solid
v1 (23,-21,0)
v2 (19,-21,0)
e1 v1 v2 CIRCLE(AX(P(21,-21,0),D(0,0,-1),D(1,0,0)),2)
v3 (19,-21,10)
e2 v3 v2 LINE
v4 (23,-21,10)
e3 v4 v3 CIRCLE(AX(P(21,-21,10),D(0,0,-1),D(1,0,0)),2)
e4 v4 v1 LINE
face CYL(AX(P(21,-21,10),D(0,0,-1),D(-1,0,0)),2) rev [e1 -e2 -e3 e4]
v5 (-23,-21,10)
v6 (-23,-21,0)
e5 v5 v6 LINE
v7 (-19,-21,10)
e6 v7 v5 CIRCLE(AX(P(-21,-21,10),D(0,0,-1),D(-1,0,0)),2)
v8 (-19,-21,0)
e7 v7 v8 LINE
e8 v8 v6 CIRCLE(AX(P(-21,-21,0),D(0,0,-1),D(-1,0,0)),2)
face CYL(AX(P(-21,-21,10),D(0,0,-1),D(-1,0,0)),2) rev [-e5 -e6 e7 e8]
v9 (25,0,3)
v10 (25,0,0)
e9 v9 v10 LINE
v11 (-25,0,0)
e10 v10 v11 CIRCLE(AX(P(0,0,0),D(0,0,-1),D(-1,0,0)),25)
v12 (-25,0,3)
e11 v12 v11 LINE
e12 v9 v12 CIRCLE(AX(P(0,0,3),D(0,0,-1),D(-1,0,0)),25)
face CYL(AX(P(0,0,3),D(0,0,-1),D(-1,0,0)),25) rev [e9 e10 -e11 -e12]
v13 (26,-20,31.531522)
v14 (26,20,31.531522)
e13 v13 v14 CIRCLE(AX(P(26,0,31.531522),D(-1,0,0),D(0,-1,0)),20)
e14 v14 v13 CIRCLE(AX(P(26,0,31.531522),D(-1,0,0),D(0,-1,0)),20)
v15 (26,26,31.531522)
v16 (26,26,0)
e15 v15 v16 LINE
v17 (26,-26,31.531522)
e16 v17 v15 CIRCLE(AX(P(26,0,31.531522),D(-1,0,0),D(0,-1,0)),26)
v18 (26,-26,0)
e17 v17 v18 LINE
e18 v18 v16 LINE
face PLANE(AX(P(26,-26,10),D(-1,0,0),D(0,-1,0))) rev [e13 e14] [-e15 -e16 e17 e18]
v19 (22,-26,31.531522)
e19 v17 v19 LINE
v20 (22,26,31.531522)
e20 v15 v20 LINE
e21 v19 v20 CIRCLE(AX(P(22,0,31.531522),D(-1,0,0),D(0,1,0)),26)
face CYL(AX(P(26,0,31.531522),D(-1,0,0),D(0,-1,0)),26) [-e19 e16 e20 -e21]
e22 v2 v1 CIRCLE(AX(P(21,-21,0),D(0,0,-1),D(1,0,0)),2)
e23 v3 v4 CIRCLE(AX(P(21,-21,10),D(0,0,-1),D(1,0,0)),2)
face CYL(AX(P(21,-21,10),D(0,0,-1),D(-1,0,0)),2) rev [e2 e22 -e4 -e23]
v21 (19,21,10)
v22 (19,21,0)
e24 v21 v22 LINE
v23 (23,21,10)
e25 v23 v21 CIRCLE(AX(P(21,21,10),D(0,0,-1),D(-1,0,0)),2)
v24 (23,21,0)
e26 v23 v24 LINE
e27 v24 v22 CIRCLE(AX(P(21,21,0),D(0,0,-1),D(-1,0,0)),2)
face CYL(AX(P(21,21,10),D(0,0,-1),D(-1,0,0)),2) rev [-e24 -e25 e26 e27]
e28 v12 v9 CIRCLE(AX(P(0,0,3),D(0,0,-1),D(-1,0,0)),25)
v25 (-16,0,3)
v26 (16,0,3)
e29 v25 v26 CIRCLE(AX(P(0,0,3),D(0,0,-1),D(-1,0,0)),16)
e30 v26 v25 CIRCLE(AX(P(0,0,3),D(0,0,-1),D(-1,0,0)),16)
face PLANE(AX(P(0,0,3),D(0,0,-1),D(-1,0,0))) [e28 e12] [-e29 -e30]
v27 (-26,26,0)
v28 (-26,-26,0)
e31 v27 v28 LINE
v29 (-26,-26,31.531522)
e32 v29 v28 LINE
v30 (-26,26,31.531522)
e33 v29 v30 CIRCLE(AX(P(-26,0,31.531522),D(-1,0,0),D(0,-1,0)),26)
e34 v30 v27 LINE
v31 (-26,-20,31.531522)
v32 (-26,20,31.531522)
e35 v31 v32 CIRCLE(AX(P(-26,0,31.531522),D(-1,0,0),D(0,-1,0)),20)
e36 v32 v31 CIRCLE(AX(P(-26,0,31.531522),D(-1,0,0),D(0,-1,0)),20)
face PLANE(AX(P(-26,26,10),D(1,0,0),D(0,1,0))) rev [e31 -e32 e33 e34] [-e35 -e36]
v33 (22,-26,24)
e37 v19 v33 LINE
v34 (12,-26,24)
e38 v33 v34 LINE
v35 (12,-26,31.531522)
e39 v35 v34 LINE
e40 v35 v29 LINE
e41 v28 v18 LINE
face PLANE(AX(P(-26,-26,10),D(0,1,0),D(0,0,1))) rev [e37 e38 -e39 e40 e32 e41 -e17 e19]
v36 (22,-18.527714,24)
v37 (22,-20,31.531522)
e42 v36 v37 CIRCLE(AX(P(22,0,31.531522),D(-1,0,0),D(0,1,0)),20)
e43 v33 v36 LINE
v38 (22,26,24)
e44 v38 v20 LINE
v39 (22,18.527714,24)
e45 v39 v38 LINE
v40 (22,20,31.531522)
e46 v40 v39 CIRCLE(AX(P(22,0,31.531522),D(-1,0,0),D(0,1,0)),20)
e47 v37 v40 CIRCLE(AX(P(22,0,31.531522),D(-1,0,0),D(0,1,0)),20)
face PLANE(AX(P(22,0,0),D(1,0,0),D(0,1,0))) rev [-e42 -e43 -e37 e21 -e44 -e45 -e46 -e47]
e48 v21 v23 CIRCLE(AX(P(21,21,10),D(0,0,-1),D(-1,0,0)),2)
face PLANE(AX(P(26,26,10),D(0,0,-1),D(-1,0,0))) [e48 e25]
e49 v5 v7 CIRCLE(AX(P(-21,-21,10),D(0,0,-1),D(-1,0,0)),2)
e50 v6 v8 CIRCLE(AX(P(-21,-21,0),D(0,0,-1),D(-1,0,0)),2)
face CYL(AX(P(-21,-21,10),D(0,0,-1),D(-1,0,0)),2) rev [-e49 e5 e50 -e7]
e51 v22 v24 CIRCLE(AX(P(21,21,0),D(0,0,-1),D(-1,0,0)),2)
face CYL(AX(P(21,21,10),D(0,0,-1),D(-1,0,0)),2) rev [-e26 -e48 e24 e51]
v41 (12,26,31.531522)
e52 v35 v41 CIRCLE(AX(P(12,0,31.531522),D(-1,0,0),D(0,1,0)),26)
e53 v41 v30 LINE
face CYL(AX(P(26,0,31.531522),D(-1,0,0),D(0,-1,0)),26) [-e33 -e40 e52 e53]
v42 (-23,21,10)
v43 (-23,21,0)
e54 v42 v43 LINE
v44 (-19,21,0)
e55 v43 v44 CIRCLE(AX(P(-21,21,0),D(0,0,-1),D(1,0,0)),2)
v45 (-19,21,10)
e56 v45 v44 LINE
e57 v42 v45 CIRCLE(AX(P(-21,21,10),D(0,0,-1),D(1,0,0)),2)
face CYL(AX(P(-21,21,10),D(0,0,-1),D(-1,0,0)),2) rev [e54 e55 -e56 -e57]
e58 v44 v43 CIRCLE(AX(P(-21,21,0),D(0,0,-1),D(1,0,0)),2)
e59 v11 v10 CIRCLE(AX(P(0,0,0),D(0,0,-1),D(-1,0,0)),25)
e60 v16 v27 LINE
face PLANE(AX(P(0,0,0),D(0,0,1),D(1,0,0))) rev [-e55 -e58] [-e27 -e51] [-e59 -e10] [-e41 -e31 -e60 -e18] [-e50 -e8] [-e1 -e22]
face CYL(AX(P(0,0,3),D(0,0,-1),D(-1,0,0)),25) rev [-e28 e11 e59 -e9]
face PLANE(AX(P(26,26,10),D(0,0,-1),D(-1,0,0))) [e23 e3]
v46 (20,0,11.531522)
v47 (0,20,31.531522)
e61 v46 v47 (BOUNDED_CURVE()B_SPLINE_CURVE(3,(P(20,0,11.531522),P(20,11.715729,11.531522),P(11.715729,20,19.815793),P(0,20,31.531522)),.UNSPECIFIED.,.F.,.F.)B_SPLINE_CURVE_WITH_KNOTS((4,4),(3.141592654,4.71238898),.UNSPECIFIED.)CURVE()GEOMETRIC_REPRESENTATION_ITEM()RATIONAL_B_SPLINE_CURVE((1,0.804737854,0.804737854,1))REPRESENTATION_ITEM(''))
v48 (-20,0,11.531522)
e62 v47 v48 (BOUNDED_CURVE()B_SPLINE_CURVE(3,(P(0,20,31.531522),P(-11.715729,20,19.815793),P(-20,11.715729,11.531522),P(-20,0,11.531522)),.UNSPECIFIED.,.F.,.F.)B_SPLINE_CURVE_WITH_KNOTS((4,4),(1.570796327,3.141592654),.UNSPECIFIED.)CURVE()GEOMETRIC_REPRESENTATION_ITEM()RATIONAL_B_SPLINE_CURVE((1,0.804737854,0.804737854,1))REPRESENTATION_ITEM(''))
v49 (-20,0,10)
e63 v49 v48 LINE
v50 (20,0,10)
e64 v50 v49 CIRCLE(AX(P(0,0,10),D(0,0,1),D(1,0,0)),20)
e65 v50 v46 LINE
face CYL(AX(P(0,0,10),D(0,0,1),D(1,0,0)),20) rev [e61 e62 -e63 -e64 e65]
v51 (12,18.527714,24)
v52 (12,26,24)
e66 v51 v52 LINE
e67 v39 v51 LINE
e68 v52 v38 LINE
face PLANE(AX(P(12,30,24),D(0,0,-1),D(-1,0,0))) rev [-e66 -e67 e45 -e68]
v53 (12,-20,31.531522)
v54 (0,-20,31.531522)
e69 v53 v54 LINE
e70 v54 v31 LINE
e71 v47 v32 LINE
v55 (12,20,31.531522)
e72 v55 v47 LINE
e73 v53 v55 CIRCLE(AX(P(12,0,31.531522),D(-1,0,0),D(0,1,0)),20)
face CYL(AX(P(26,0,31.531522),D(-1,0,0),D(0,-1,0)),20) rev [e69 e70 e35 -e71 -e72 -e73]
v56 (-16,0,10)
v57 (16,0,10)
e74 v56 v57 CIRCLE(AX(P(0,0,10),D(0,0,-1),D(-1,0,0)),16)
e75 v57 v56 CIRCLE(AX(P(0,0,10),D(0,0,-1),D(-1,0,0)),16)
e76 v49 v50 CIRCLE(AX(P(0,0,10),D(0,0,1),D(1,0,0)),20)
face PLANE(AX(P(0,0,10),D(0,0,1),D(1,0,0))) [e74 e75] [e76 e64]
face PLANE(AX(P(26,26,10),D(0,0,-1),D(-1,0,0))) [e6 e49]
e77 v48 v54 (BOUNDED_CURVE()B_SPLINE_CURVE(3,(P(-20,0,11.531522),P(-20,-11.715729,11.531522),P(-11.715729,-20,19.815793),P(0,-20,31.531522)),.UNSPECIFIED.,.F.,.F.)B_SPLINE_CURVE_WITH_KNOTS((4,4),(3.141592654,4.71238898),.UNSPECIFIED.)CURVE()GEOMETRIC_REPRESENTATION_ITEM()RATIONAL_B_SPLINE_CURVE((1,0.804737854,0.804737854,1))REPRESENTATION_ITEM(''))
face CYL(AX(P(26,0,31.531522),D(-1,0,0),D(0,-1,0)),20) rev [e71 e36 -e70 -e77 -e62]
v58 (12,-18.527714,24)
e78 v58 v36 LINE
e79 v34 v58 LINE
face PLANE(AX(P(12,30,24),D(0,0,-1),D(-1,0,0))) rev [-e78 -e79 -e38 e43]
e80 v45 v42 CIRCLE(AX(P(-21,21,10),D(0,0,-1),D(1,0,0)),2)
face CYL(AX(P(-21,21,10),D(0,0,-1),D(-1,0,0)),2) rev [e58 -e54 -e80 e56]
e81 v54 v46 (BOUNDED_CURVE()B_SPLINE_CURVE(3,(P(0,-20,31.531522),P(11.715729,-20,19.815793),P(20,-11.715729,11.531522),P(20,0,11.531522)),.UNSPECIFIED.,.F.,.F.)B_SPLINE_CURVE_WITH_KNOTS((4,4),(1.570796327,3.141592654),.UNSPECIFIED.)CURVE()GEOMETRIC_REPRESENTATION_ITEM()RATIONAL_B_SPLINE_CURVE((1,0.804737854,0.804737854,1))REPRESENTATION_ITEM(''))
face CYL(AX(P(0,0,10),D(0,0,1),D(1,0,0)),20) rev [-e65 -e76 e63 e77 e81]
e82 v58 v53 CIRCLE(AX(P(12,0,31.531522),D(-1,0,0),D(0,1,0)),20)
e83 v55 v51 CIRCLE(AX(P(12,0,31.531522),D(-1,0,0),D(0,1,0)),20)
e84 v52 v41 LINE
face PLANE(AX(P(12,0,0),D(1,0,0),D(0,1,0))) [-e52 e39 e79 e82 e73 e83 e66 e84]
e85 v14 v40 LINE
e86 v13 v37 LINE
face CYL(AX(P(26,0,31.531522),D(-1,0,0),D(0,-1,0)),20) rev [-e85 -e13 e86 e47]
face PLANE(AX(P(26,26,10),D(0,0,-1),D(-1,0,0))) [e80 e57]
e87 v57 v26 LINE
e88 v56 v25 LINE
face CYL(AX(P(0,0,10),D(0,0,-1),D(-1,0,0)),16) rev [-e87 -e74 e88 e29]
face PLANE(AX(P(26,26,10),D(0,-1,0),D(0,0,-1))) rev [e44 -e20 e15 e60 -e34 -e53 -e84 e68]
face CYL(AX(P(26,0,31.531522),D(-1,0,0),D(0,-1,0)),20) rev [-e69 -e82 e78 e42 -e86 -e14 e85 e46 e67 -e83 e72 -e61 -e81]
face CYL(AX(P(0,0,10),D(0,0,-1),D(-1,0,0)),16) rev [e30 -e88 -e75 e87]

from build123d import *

# Parameters (mm, degrees)
SKETCH3_W           = 52
SKETCH3_H           = 52
BOSS_EXTRUDE1_DEPTH = 10
SKETCH4_R           = 2
CUT_EXTRUDE1_DEPTH  = 10
SKETCH5_R           = 25
CUT_EXTRUDE2_DEPTH  = 3
SKETCH6_R           = 16
CUT_EXTRUDE3_DEPTH  = 38.429934544
SKETCH8_W           = 21.53152206
SKETCH8_H           = 52
BOSS_EXTRUDE2_DEPTH = 52
SKETCH9_R           = 20
CUT_EXTRUDE4_DEPTH  = 21.53152206
BOSS_EXTRUDE3_DEPTH = 52
SKETCH11_R          = 20
CUT_EXTRUDE5_DEPTH  = 52
SKETCH12_W          = 34.659031173
SKETCH12_H          = 60
CUT_EXTRUDE6_DEPTH  = 10


with BuildPart() as part:
    # Sketch3 → Boss-Extrude1 (new body)
    with BuildSketch(Plane.XY):
        Rectangle(SKETCH3_W, SKETCH3_H)
    extrude(amount=BOSS_EXTRUDE1_DEPTH)

    # Sketch4 → Cut-Extrude1 (cut)
    with BuildSketch(Plane(origin=(0, 0, 0), x_dir=(-1, 0, 0), z_dir=(0, 0, -1))):
        with Locations((-21, 21)):
            Circle(SKETCH4_R)
        with Locations(Location((21, 21, 0), (0, 0, 180))):
            Circle(SKETCH4_R)
        with Locations((21, -21)):
            Circle(SKETCH4_R)
        with Locations(Location((-21, -21, 0), (0, 0, 180))):
            Circle(SKETCH4_R)
    extrude(amount=-CUT_EXTRUDE1_DEPTH, mode=Mode.SUBTRACT)

    # Sketch5 → Cut-Extrude2 (cut)
    with BuildSketch(Plane(origin=(0, 0, 0), x_dir=(-1, 0, 0), z_dir=(0, 0, -1))):
        Circle(SKETCH5_R)
    extrude(amount=-CUT_EXTRUDE2_DEPTH, mode=Mode.SUBTRACT)

    # Sketch6 → Cut-Extrude3 (cut, through all)
    with BuildSketch(Plane(origin=(0, 0, 3), x_dir=(-1, 0, 0), z_dir=(0, 0, -1))):
        Circle(SKETCH6_R)
    extrude(amount=-CUT_EXTRUDE3_DEPTH, mode=Mode.SUBTRACT)

    # Sketch8 → Boss-Extrude2 (add)
    with BuildSketch(Plane.ZY.offset(26)):
        with Locations((20.76576103, 0)):
            Rectangle(SKETCH8_W, SKETCH8_H)
    extrude(amount=-BOSS_EXTRUDE2_DEPTH)

    # Sketch9 → Cut-Extrude4 (cut)
    with BuildSketch(Plane.XY.offset(31.53152206)):
        Circle(SKETCH9_R)
    extrude(amount=-CUT_EXTRUDE4_DEPTH, mode=Mode.SUBTRACT)

    # Sketch10 → Boss-Extrude3 (add)
    with BuildSketch(Plane.ZY.offset(26)):
        with BuildLine():
            Line((31.53152206, 26), (31.53152206, -26))
            ThreePointArc((31.53152206, -26), (57.53152206, 0), (31.53152206, 26))
        make_face()
    extrude(amount=-BOSS_EXTRUDE3_DEPTH)

    # Sketch11 → Cut-Extrude5 (cut)
    with BuildSketch(Plane.ZY.offset(26)):
        with Locations(Location((31.53152206, 0, 0), (0, 0, 270))):
            Circle(SKETCH11_R)
    extrude(amount=-CUT_EXTRUDE5_DEPTH, mode=Mode.SUBTRACT)

    # Sketch12 → Cut-Extrude6 (cut)
    with BuildSketch(Plane(origin=(22, 0, 0), x_dir=(0, 0, -1), z_dir=(1, 0, 0))):
        with Locations((-41.329515587, 0)):
            Rectangle(SKETCH12_W, SKETCH12_H)
    extrude(amount=-CUT_EXTRUDE6_DEPTH, mode=Mode.SUBTRACT)


solid = part.part
